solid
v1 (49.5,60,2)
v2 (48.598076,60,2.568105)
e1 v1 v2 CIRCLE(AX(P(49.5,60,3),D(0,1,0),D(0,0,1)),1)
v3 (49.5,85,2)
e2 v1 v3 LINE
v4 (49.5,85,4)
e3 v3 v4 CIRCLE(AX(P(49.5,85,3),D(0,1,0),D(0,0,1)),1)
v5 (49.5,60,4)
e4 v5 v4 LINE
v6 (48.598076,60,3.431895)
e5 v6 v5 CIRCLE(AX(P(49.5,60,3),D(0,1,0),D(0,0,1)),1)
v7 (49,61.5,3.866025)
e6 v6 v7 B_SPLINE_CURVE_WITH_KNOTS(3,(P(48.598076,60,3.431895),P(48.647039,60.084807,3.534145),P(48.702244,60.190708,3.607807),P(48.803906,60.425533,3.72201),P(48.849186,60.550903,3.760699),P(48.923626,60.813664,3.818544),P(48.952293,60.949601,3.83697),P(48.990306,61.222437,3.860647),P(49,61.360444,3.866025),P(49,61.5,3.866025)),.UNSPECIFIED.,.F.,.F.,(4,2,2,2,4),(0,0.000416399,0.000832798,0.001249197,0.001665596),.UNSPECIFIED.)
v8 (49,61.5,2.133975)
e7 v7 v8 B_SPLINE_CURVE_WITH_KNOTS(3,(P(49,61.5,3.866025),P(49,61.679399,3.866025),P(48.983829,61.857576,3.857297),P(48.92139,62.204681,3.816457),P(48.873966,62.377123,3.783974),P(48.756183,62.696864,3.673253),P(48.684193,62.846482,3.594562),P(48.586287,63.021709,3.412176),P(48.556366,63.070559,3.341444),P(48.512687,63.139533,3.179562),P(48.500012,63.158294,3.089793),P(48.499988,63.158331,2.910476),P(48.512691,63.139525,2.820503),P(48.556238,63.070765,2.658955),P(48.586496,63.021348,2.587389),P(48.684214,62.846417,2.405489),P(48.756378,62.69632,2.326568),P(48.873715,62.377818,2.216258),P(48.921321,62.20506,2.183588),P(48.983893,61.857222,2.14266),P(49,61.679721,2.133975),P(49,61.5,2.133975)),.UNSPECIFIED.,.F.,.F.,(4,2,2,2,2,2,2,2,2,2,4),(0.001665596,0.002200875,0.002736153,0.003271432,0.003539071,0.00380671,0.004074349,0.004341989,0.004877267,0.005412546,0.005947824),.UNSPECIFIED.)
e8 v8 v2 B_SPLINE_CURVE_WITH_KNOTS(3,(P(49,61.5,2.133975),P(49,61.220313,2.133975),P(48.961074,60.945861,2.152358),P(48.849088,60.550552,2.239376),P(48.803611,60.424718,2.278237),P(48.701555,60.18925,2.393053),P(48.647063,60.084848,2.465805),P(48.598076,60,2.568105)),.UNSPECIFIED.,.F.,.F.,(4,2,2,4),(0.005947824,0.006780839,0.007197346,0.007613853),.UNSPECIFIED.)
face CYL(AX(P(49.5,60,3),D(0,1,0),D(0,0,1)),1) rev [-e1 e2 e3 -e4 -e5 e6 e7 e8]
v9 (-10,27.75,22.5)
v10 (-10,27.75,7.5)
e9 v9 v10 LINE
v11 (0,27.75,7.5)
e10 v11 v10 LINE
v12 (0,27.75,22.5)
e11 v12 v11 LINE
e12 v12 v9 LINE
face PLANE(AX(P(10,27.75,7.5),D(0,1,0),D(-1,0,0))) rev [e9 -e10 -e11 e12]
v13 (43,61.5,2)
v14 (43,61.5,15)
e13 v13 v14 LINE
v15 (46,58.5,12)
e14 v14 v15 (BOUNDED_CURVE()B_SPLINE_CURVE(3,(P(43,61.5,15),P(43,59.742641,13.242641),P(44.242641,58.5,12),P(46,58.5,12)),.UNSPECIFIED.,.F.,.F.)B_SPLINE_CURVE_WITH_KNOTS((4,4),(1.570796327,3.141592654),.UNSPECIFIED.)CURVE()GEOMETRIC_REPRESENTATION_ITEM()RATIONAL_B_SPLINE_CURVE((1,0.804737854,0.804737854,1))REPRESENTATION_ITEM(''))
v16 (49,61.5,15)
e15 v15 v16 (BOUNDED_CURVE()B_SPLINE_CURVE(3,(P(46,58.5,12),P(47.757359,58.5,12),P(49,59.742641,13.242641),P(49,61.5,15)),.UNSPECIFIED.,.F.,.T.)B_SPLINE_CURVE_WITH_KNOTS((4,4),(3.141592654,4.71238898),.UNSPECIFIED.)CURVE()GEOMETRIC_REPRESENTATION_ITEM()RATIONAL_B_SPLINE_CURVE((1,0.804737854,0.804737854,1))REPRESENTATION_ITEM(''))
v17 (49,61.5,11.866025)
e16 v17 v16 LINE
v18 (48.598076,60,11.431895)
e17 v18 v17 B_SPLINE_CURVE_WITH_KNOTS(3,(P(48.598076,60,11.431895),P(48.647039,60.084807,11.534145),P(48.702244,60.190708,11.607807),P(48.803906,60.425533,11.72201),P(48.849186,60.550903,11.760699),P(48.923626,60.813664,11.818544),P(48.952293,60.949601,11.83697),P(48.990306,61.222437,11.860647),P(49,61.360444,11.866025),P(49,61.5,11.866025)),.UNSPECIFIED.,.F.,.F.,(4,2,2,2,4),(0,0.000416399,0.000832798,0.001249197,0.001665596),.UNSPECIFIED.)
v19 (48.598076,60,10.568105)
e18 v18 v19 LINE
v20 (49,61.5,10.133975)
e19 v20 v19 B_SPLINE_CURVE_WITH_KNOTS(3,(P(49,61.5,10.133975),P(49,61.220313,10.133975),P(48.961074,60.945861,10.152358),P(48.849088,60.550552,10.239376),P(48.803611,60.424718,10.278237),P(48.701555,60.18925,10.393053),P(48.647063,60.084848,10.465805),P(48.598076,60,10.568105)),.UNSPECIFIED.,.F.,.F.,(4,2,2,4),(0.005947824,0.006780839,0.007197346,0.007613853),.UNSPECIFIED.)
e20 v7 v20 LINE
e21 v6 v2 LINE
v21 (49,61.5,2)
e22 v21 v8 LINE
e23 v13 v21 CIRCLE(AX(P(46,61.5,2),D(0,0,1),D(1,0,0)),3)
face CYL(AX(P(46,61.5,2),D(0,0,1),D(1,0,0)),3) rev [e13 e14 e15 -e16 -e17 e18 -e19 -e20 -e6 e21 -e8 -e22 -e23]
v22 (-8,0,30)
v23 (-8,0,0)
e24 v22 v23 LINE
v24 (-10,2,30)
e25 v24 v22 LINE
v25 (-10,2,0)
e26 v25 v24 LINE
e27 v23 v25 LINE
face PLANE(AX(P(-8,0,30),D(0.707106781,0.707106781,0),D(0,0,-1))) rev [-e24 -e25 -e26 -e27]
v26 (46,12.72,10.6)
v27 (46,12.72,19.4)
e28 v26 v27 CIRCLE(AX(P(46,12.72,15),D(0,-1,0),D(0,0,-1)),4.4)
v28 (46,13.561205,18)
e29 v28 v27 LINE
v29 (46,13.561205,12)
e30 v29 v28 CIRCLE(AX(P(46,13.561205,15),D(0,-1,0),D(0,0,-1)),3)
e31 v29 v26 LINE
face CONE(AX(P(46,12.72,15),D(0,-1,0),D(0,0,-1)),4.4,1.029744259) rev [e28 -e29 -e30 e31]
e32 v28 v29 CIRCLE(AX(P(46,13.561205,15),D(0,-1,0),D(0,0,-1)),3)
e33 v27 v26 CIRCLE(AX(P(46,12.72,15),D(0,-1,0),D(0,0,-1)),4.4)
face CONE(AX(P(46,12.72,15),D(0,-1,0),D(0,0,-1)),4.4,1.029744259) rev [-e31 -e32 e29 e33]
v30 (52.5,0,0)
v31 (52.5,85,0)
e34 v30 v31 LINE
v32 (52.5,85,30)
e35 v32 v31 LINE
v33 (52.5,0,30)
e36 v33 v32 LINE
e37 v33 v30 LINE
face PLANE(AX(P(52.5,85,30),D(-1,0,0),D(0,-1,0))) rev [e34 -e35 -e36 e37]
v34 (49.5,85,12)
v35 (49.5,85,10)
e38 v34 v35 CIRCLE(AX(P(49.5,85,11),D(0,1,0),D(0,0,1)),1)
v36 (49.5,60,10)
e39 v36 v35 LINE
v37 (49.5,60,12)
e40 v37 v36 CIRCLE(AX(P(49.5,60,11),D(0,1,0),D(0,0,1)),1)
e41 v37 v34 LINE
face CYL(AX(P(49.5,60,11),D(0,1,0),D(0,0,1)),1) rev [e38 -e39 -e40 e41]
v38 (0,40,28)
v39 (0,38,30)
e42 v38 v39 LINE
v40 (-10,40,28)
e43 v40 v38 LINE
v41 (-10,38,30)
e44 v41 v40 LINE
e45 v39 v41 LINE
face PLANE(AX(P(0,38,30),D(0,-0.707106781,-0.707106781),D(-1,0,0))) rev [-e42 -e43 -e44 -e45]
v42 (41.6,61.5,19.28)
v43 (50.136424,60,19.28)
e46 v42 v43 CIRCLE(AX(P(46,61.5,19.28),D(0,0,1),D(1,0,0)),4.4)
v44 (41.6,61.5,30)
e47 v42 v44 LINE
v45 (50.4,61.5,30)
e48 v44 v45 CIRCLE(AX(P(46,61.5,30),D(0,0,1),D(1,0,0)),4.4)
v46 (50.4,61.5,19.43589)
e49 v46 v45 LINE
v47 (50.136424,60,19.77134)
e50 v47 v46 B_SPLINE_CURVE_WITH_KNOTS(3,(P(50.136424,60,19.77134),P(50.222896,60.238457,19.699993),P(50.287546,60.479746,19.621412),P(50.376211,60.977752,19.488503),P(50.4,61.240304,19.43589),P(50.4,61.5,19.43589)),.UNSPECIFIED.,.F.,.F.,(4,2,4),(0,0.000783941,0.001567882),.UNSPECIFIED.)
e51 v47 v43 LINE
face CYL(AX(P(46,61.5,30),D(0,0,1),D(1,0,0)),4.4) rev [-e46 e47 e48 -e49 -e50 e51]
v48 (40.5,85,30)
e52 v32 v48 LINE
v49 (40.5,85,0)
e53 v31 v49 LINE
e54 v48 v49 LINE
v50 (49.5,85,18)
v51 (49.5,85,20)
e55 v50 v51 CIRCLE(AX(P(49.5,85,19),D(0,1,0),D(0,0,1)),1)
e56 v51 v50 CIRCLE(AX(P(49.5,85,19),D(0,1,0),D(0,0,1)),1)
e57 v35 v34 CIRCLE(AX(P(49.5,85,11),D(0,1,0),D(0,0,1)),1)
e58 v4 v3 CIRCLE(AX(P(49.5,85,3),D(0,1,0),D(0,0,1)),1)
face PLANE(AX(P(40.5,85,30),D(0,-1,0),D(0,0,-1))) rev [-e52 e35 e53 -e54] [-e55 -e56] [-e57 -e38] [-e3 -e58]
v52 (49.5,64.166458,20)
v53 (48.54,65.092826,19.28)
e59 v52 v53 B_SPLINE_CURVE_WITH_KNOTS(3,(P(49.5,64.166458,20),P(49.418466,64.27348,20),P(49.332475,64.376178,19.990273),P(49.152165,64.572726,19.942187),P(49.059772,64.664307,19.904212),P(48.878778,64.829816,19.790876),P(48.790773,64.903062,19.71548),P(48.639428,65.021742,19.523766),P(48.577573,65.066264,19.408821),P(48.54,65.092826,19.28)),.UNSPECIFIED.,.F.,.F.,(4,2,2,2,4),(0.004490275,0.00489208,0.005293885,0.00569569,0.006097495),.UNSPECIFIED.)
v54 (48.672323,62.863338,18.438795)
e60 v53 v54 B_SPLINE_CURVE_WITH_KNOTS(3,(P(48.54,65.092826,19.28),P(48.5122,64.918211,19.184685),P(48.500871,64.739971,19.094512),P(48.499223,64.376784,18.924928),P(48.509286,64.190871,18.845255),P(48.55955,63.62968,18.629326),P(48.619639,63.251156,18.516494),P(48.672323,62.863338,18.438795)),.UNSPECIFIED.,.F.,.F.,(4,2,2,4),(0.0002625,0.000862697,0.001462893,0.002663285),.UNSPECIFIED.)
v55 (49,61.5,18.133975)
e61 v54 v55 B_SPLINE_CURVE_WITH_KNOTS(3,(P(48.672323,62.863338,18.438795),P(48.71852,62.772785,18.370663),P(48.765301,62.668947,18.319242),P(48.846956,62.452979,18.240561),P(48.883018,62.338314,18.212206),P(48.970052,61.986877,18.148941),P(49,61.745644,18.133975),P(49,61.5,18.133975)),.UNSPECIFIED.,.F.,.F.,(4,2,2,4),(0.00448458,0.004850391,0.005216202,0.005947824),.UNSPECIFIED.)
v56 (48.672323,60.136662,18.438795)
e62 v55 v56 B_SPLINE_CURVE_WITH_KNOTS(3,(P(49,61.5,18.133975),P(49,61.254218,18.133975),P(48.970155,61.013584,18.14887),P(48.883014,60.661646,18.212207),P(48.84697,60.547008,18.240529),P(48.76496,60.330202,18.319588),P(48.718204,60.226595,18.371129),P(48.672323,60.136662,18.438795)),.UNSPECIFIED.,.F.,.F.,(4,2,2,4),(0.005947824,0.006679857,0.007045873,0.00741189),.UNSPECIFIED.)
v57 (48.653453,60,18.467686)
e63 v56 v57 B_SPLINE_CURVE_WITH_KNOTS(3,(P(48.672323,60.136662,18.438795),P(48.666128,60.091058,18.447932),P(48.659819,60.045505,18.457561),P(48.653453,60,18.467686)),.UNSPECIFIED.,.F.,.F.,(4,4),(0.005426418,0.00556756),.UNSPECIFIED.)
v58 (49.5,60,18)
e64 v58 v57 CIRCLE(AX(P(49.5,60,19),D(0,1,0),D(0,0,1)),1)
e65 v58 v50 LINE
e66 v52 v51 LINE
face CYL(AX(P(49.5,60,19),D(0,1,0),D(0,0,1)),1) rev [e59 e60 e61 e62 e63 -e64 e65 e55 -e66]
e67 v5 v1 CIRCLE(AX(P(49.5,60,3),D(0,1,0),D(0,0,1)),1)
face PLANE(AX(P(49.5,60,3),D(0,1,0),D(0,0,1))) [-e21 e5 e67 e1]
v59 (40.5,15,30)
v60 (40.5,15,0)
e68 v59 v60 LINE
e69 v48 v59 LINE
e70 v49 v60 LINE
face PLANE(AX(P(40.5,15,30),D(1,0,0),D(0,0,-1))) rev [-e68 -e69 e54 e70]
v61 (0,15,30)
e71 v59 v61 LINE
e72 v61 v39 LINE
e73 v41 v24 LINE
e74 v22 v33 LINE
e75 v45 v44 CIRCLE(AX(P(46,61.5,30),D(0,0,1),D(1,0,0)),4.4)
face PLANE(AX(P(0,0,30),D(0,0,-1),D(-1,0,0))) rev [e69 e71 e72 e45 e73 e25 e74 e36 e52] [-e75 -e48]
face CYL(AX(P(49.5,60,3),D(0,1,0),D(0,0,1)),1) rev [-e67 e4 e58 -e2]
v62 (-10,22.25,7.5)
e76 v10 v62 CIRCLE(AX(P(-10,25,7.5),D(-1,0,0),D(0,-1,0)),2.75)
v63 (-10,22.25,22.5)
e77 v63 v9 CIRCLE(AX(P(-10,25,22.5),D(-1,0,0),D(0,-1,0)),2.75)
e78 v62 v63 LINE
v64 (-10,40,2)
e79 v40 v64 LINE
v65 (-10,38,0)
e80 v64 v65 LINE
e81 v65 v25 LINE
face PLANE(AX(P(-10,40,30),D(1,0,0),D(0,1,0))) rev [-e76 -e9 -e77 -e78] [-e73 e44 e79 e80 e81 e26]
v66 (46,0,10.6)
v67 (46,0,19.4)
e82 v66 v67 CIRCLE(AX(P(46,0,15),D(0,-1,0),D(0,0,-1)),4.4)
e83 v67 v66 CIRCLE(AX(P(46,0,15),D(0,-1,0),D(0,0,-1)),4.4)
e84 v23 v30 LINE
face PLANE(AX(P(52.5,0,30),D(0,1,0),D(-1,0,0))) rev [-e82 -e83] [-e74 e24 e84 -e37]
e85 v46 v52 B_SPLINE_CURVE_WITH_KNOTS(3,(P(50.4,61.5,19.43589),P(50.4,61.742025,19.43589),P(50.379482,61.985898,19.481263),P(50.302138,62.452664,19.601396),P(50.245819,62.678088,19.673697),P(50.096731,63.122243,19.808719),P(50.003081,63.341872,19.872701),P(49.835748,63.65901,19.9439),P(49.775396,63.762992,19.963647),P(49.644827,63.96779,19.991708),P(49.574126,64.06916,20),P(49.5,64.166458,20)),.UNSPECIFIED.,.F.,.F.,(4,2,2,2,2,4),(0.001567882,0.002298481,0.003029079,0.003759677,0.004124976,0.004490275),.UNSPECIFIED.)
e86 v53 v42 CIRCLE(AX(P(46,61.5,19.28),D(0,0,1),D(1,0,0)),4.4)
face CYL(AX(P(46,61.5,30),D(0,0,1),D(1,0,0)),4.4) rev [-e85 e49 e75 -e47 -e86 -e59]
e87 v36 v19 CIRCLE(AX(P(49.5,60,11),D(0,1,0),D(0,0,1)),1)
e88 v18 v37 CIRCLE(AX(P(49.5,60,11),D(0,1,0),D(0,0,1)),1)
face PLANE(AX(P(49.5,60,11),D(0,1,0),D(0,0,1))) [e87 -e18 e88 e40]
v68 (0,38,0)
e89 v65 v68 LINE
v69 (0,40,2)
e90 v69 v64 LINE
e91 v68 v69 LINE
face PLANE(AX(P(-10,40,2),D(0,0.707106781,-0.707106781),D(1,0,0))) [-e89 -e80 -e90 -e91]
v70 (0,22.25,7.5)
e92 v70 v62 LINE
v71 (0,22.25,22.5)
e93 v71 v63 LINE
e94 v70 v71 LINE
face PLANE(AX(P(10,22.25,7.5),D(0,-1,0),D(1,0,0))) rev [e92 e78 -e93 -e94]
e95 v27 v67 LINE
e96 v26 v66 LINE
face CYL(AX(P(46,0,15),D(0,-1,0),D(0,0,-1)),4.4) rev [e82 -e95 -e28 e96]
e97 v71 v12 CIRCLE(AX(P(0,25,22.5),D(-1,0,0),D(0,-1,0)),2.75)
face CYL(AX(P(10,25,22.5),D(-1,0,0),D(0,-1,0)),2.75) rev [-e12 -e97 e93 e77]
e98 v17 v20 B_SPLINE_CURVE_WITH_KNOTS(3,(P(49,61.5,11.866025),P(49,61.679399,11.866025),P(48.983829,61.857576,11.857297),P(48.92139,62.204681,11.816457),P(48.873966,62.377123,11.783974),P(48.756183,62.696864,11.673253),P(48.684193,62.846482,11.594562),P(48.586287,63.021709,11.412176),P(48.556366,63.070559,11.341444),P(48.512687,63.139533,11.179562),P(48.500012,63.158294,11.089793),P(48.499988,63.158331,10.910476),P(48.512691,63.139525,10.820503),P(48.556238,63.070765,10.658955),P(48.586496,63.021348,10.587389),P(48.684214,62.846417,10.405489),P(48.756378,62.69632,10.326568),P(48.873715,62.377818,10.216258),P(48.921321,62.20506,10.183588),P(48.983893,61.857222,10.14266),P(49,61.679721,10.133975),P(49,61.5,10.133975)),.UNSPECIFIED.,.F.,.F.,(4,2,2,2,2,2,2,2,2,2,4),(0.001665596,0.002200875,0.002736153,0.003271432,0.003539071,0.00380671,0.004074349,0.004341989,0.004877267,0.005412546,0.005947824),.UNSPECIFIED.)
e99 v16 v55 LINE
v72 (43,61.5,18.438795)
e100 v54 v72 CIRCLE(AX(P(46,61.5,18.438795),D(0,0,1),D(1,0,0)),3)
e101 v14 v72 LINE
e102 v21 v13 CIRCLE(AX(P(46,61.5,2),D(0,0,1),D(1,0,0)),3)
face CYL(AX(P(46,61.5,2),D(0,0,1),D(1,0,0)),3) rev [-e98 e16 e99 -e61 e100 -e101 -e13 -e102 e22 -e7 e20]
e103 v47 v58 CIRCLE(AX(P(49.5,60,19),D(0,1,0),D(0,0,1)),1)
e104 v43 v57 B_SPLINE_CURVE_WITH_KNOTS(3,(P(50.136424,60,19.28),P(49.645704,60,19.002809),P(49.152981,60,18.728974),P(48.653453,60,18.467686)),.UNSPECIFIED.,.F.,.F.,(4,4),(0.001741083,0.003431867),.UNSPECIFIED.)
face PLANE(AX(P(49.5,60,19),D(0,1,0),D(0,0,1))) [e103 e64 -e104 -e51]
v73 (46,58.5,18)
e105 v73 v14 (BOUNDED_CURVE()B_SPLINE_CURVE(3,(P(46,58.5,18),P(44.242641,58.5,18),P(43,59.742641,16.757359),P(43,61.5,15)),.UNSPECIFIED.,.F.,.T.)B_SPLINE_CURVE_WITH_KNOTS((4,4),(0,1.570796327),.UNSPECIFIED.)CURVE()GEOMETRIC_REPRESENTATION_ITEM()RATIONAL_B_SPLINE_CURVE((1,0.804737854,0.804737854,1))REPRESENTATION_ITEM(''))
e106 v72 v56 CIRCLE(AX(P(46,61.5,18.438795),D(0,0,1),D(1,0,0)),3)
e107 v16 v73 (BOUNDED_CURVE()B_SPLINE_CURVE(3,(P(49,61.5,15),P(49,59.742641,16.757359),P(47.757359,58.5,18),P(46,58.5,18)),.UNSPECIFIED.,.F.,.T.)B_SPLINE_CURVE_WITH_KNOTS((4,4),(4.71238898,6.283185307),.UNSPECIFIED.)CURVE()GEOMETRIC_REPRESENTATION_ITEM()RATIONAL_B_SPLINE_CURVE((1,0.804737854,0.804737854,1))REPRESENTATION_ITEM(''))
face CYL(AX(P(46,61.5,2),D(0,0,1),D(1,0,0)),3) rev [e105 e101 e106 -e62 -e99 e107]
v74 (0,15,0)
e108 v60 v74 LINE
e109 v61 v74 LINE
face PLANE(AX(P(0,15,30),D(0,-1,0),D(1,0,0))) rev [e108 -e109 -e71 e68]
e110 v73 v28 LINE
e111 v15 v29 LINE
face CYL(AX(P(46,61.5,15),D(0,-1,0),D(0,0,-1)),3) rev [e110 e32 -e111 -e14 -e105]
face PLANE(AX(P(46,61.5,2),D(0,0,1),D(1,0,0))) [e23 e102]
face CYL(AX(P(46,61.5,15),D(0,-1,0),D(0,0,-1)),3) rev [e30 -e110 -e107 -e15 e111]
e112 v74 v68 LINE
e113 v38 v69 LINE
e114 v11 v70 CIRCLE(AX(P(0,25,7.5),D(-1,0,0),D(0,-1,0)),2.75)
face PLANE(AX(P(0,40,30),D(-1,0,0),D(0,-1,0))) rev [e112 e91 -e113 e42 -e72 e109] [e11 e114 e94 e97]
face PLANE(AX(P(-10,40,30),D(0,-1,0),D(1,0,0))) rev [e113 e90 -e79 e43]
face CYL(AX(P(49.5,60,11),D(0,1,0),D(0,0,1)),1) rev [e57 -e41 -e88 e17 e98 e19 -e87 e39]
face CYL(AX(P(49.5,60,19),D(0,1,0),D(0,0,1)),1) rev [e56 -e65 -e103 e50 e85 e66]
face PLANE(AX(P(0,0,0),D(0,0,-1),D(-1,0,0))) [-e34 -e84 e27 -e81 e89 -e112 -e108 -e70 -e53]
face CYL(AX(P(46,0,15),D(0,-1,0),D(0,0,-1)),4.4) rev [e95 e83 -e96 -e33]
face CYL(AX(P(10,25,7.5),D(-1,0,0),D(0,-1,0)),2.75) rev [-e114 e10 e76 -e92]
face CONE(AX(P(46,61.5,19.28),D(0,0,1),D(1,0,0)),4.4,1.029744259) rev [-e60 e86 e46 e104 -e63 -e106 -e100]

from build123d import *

# Parameters (mm, degrees)
BOSS_EXTRUDE1_DEPTH     = 30
SKETCH2_R               = 1
CUT_EXTRUDE1_DEPTH      = 25
SKETCH3_R               = 3
CUT_EXTRUDE2_DEPTH      = 28
SKETCH4_R               = 3
CUT_EXTRUDE3_DEPTH      = 61.5
CUT_EXTRUDE4_DEPTH      = 20
CHAMFER1_SIZE           = 2
G1_8_TAPPED_HOLE1_D     = 8.8
G1_8_TAPPED_HOLE1_DEPTH = 12.72
G1_8_TAPPED_HOLE1_TIP   = 2.643786724
G1_8_TAPPED_HOLE2_D     = 8.8
G1_8_TAPPED_HOLE2_DEPTH = 10.72
G1_8_TAPPED_HOLE2_TIP   = 2.643786724


with BuildPart() as part:
    # Sketch1 → Boss-Extrude1 (new body)
    with BuildSketch(Plane.XY):
        Polygon((-10, 40), (-10, 0), (52.5, 0), (52.5, 85), (40.5, 85), (40.5, 15), (0, 15), (0, 40), align=None)
    extrude(amount=BOSS_EXTRUDE1_DEPTH)

    # Sketch2 → Cut-Extrude1 (cut)
    with BuildSketch(Plane(origin=(0, 85, 0), x_dir=(1, 0, 0), z_dir=(0, 1, 0))):
        with Locations(Location((49.5, -3, 0), (0, 0, 270))):
            Circle(SKETCH2_R)
        with Locations(Location((49.5, -11, 0), (0, 0, 270))):
            Circle(SKETCH2_R)
        with Locations(Location((49.5, -19, 0), (0, 0, 270))):
            Circle(SKETCH2_R)
    extrude(amount=-CUT_EXTRUDE1_DEPTH, mode=Mode.SUBTRACT)

    # Sketch3 → Cut-Extrude2 (cut)
    with BuildSketch(Plane.XY.offset(30)):
        with Locations((46, 61.5)):
            Circle(SKETCH3_R)
    extrude(amount=-CUT_EXTRUDE2_DEPTH, mode=Mode.SUBTRACT)

    # Sketch4 → Cut-Extrude3 (cut)
    with BuildSketch(Plane.XZ):
        with Locations(Location((46, 15, 0), (0, 0, 270))):
            Circle(SKETCH4_R)
    extrude(amount=-CUT_EXTRUDE3_DEPTH, mode=Mode.SUBTRACT)

    # Sketch5 → Cut-Extrude4 (cut)
    with BuildSketch(Plane.ZY.offset(10)):
        with BuildLine():
            Line((7.5, 27.75), (22.5, 27.75))
            ThreePointArc((22.5, 27.75), (25.25, 25), (22.5, 22.25))
            Line((22.5, 22.25), (7.5, 22.25))
            ThreePointArc((7.5, 22.25), (4.75, 25), (7.5, 27.75))
        make_face()
    extrude(amount=-CUT_EXTRUDE4_DEPTH, mode=Mode.SUBTRACT)

    # Chamfer1
    chamfer1_edges = [part.edges().sort_by_distance(p)[0] for p in [
        (-5, 40, 0),
        (-10, 0, 15),
        (-5, 40, 30),
    ]]
    chamfer(chamfer1_edges, length=CHAMFER1_SIZE)

    # G1/8 Tapped Hole1
    with Locations(Plane.XZ):
        with Locations((46, 15)):
            Hole(G1_8_TAPPED_HOLE1_D / 2, depth=G1_8_TAPPED_HOLE1_DEPTH)
            with Locations((0, 0, -(G1_8_TAPPED_HOLE1_DEPTH + G1_8_TAPPED_HOLE1_TIP / 2))):  # 118° drill point
                Cone(0, G1_8_TAPPED_HOLE1_D / 2, G1_8_TAPPED_HOLE1_TIP, mode=Mode.SUBTRACT)

    # G1/8 Tapped Hole2
    with Locations(Plane.XY.offset(30)):
        with Locations((46, 61.5)):
            Hole(G1_8_TAPPED_HOLE2_D / 2, depth=G1_8_TAPPED_HOLE2_DEPTH)
            with Locations((0, 0, -(G1_8_TAPPED_HOLE2_DEPTH + G1_8_TAPPED_HOLE2_TIP / 2))):  # 118° drill point
                Cone(0, G1_8_TAPPED_HOLE2_D / 2, G1_8_TAPPED_HOLE2_TIP, mode=Mode.SUBTRACT)


solid = part.part
